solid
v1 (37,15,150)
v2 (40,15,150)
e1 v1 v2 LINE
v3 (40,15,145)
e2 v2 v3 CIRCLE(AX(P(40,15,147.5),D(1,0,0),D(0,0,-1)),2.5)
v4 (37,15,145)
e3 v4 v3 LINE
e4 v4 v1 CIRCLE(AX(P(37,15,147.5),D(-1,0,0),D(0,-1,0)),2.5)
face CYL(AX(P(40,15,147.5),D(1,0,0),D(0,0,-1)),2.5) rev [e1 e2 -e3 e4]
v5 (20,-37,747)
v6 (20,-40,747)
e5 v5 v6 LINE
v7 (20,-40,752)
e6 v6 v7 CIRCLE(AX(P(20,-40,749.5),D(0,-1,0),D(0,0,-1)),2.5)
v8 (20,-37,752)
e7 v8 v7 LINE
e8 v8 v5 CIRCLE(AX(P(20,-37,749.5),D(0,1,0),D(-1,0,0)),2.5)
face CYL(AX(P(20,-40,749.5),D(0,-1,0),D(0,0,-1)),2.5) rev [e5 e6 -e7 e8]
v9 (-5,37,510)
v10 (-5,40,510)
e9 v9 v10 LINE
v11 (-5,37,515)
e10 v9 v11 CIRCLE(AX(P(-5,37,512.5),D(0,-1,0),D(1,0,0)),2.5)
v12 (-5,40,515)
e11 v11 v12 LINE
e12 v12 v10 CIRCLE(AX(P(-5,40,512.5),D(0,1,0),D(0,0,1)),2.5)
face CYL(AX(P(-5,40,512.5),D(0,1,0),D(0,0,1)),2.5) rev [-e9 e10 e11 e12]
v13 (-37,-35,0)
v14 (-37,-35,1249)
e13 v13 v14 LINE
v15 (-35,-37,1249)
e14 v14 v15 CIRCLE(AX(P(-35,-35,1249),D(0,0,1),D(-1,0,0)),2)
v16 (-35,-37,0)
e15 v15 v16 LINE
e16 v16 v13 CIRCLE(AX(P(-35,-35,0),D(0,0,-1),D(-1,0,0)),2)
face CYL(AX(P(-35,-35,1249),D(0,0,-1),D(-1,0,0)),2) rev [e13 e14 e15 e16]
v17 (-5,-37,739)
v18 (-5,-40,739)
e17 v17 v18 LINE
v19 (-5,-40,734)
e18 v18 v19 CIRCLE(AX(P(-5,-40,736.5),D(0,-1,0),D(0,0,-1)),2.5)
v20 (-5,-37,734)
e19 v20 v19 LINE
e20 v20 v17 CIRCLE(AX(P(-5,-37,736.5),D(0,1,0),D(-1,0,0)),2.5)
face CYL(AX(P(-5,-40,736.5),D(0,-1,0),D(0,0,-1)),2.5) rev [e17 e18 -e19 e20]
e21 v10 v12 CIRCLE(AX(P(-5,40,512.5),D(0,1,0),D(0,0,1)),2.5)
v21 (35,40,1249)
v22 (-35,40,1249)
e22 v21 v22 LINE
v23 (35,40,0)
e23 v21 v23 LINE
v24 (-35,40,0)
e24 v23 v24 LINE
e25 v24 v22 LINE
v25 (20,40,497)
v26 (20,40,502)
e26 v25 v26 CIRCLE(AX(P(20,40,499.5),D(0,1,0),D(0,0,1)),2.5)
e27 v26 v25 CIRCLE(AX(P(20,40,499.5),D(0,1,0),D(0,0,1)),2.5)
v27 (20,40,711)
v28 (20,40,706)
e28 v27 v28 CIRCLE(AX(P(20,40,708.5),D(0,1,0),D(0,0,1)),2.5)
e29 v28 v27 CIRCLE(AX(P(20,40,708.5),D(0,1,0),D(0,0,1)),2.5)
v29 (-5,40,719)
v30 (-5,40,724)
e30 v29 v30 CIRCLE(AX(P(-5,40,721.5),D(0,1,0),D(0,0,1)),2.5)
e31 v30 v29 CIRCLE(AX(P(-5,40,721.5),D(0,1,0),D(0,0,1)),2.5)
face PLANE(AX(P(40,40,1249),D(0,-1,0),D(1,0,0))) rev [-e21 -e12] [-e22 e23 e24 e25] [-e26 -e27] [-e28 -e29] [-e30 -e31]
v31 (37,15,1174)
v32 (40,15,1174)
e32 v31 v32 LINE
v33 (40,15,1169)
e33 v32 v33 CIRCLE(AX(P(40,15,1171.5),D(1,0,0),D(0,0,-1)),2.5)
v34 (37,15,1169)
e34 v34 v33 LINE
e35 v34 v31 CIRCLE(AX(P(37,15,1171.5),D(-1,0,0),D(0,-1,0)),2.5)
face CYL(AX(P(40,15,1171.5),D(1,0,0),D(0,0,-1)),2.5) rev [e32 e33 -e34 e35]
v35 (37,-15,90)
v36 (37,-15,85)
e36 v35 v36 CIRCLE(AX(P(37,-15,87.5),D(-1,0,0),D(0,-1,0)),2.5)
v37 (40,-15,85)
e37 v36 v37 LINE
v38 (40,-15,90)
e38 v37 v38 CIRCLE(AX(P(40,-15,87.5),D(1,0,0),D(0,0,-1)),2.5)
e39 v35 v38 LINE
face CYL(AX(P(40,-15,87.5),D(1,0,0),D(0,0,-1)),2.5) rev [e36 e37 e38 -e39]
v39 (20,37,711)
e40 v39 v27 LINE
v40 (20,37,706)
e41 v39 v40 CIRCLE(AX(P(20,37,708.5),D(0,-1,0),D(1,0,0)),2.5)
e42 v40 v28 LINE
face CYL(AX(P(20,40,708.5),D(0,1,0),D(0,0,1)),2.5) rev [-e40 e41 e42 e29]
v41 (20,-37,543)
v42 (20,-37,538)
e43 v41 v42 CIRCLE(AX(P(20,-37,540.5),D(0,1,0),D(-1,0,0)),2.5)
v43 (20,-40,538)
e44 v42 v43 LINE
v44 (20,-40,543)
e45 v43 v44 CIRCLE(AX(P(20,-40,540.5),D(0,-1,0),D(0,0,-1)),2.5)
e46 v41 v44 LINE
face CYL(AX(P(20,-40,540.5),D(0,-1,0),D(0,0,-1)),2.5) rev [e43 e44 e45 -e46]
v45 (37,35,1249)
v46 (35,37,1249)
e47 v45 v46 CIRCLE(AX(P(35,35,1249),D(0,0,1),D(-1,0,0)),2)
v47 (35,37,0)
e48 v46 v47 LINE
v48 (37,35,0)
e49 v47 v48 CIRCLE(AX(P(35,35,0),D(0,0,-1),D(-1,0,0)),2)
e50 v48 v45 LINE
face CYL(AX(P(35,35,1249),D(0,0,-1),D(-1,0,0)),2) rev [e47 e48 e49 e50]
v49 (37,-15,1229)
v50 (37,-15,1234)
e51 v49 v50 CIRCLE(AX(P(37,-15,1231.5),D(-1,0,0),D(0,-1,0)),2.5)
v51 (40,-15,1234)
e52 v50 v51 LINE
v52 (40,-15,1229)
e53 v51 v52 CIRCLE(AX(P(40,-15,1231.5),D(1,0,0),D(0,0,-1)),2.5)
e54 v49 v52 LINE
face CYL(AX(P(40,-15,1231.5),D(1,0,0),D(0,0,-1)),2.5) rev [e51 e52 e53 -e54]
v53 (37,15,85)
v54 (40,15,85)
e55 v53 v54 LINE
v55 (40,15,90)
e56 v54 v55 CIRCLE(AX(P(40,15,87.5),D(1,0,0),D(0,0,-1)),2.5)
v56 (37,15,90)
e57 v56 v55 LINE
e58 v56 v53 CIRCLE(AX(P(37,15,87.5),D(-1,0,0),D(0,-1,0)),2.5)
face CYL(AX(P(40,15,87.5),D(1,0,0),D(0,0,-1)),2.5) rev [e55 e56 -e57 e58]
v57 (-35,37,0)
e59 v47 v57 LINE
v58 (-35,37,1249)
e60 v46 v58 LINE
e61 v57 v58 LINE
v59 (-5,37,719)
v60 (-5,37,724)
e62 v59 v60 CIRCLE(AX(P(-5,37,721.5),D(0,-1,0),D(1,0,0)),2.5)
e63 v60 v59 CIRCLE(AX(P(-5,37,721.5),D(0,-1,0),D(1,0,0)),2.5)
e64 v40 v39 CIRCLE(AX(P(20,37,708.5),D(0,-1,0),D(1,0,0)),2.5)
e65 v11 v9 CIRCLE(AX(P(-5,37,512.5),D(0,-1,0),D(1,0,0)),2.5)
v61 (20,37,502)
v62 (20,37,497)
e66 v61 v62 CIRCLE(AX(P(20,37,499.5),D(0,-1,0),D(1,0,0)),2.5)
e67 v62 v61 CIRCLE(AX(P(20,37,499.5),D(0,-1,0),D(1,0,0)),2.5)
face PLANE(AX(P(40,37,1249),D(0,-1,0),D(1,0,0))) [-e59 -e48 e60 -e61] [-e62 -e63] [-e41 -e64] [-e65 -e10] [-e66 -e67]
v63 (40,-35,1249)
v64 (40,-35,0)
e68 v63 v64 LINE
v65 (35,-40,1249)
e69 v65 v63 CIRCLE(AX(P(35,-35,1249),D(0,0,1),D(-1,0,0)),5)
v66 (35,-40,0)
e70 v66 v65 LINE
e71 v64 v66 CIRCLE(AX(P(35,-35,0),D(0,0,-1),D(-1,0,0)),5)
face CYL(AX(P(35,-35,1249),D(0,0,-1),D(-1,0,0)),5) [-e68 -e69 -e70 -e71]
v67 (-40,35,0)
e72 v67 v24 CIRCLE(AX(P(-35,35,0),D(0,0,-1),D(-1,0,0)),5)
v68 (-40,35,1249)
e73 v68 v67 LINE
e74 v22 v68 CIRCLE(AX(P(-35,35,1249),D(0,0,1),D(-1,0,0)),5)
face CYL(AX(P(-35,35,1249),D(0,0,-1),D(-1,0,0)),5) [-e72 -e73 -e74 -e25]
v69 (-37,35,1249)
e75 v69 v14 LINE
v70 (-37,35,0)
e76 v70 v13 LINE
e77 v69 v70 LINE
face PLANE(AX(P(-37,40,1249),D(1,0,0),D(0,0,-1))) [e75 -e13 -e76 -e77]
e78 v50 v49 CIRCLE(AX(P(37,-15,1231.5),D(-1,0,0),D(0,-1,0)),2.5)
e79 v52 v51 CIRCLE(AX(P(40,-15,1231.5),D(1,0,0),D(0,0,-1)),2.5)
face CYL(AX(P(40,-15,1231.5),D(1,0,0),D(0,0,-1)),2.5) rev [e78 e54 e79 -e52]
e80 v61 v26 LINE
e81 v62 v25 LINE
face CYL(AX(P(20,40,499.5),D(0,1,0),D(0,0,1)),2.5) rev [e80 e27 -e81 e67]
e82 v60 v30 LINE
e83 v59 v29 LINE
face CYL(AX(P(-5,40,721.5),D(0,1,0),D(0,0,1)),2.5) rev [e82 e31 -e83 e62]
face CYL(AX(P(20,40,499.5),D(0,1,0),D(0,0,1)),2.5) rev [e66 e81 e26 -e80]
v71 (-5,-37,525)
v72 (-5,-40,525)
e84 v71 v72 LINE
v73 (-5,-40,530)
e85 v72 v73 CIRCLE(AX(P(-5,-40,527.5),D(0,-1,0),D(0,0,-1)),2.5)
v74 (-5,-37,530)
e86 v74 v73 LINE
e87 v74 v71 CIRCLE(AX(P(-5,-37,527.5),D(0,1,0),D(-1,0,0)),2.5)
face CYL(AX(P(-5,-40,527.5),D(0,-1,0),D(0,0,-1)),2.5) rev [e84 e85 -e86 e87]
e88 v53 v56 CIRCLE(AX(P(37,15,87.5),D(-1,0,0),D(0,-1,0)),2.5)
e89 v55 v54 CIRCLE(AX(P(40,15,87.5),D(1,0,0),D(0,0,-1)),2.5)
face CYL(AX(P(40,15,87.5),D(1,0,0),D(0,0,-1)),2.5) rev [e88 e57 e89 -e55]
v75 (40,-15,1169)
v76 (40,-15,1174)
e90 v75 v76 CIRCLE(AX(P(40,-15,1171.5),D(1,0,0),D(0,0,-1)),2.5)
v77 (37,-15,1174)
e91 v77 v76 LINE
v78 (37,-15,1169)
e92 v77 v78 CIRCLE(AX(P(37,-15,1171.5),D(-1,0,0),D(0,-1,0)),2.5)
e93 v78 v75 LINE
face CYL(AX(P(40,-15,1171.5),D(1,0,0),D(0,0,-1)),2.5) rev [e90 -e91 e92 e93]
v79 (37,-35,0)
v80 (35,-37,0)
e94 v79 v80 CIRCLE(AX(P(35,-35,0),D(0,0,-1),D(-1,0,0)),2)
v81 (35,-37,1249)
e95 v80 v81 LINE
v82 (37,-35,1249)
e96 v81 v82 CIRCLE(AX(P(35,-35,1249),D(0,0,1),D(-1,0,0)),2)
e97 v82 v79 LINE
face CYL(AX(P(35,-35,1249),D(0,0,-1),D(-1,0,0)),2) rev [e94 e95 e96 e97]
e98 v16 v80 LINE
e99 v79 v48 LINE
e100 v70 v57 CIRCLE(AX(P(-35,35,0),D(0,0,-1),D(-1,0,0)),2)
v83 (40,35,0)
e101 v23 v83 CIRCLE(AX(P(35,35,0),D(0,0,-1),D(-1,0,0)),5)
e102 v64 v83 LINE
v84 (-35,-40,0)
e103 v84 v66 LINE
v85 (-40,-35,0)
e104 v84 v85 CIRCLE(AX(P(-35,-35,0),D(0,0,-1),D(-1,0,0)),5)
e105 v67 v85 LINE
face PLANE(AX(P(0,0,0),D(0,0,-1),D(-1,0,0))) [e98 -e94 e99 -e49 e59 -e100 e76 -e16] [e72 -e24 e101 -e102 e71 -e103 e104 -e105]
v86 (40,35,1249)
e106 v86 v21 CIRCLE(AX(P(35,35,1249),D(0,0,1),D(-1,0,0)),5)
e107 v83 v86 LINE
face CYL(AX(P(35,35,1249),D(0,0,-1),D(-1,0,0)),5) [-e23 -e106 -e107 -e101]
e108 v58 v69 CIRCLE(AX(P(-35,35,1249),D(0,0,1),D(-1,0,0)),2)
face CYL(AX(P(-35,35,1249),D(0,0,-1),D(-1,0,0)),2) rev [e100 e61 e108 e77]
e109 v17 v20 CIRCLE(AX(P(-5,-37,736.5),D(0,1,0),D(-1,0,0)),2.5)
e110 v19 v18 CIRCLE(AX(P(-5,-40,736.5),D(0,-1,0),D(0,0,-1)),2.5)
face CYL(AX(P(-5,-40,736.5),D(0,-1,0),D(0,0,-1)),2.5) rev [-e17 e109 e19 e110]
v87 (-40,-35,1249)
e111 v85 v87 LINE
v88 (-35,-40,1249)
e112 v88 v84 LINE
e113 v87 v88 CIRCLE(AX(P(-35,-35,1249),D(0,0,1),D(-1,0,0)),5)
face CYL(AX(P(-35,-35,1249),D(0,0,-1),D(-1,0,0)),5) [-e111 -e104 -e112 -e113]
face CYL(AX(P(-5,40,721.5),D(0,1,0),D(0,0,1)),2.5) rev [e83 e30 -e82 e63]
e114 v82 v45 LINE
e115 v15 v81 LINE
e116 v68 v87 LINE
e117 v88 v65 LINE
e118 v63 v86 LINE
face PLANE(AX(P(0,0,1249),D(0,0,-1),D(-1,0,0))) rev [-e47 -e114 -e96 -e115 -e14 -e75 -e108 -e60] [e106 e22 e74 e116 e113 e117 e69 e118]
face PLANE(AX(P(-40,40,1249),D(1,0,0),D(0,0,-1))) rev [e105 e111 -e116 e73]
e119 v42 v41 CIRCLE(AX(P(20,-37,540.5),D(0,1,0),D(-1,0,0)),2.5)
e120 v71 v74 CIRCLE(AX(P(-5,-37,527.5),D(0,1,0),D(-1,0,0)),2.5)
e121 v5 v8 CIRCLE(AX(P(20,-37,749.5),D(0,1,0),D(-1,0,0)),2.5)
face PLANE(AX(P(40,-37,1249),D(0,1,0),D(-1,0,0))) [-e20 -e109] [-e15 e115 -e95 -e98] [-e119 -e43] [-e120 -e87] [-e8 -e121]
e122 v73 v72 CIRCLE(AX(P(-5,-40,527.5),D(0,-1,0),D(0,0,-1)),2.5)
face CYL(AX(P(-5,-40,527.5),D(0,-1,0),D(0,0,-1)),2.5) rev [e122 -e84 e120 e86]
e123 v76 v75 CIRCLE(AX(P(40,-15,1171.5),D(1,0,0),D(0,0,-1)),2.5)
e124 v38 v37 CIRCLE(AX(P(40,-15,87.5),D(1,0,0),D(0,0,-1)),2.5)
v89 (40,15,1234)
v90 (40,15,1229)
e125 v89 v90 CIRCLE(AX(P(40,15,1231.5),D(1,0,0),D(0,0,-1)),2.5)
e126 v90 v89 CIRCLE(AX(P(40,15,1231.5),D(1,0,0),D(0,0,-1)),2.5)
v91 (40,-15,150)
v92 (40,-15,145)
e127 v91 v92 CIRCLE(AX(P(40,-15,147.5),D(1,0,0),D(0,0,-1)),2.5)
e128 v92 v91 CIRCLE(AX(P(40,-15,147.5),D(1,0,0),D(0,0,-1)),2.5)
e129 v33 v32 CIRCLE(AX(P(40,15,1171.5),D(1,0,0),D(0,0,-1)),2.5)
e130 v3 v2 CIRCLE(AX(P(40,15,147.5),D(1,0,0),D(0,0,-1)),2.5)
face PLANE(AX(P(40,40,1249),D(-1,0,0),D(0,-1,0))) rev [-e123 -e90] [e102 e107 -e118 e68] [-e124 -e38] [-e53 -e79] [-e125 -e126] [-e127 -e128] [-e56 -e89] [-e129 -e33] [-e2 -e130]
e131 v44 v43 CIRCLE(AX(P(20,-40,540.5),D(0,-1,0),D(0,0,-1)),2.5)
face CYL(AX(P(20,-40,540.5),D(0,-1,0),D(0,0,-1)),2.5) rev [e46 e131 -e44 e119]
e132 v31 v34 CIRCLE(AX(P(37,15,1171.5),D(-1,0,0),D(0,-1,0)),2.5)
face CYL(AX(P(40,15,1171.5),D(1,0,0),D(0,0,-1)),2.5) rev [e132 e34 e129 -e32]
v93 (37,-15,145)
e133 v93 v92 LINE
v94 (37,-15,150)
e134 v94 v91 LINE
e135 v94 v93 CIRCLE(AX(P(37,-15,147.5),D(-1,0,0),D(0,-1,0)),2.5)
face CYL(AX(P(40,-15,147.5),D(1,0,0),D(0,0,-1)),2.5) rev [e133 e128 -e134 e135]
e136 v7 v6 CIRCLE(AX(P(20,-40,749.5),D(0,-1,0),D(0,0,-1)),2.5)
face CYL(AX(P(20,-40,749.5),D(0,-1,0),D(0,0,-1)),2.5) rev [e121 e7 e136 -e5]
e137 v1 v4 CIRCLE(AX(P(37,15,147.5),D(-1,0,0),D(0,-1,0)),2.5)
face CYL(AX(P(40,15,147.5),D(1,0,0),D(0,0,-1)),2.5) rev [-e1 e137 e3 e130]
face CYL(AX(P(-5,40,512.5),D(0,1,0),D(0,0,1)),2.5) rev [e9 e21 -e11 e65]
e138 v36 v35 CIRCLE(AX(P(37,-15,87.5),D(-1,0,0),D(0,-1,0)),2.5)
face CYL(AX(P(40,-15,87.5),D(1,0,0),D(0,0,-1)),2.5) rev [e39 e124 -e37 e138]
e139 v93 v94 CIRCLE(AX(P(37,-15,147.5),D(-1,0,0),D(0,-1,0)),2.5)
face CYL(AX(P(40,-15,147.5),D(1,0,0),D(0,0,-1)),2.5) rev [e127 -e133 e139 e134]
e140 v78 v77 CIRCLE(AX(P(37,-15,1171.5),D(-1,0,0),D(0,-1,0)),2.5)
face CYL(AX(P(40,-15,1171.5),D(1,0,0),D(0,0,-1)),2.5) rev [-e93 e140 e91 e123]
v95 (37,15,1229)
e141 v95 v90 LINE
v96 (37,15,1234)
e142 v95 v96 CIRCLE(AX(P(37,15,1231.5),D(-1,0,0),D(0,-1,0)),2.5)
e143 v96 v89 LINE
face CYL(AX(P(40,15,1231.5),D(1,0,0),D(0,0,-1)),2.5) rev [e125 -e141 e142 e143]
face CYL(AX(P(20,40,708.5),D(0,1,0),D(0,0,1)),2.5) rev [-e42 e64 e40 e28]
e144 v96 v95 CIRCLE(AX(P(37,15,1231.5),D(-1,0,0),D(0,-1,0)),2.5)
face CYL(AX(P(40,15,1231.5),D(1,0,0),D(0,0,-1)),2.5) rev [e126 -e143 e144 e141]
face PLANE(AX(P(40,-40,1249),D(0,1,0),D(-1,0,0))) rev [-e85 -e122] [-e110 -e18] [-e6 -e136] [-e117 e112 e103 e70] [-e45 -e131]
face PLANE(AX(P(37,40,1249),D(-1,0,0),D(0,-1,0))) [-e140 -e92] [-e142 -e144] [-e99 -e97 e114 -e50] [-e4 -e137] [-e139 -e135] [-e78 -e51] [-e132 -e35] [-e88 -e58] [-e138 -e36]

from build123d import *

# Parameters (mm, degrees)
SKETCH_1_W             = 80
SKETCH_1_H             = 80
EXTRUDE_1_DEPTH        = 1249
FILLET_1_R             = 5
SHELL_1_T              = -3
HOLE_WIZARD_M6_1_D     = 5
HOLE_WIZARD_M6_1_DEPTH = 15
HOLE_WIZARD_M6_1_TIP   = 1.502151548
HOLE_WIZARD_M6_2_D     = 5
HOLE_WIZARD_M6_2_DEPTH = 15
HOLE_WIZARD_M6_2_TIP   = 1.502151548
HOLE_WIZARD_M6_3_D     = 5
HOLE_WIZARD_M6_3_DEPTH = 15
HOLE_WIZARD_M6_3_TIP   = 1.502151548


with BuildPart() as part:
    # 草图1 → 凸台-拉伸1 (new body)
    with BuildSketch(Plane.XY):
        Rectangle(SKETCH_1_W, SKETCH_1_H)
    extrude(amount=EXTRUDE_1_DEPTH)

    # 圆角1
    fillet_1_edges = [part.edges().sort_by_distance(p)[0] for p in [
        (-40, 40, 624.5),
        (40, 40, 624.5),
        (40, -40, 624.5),
        (-40, -40, 624.5),
    ]]
    fillet(fillet_1_edges, radius=FILLET_1_R)

    # 抽壳1
    shell_1_openings = [part.faces().sort_by_distance(p)[0] for p in [
        (0, 0, 1249),
        (0, 0, 0),
    ]]
    offset(amount=SHELL_1_T, openings=shell_1_openings, kind=Kind.INTERSECTION)

    # M6 螺纹孔1
    with Locations(Plane(origin=(40, 0, 0), x_dir=(0, 0, -1), z_dir=(1, 0, 0))):
        with Locations((-147.5, 15), (-87.5, 15), (-87.5, -15), (-147.5, -15), (-1171.5, 15), (-1171.5, -15), (-1231.5, -15), (-1231.5, 15)):
            Hole(HOLE_WIZARD_M6_1_D / 2, depth=HOLE_WIZARD_M6_1_DEPTH)
            with Locations((0, 0, -(HOLE_WIZARD_M6_1_DEPTH + HOLE_WIZARD_M6_1_TIP / 2))):  # 118° drill point
                Cone(0, HOLE_WIZARD_M6_1_D / 2, HOLE_WIZARD_M6_1_TIP, mode=Mode.SUBTRACT)

    # M6 螺纹孔2
    with Locations(Plane(origin=(0, -40, 0), x_dir=(-1, 0, 0), z_dir=(0, -1, 0))):
        with Locations((-20, -749.5), (5, -736.5), (-20, -540.5), (5, -527.5)):
            Hole(HOLE_WIZARD_M6_2_D / 2, depth=HOLE_WIZARD_M6_2_DEPTH)
            with Locations((0, 0, -(HOLE_WIZARD_M6_2_DEPTH + HOLE_WIZARD_M6_2_TIP / 2))):  # 118° drill point
                Cone(0, HOLE_WIZARD_M6_2_D / 2, HOLE_WIZARD_M6_2_TIP, mode=Mode.SUBTRACT)

    # M6 螺纹孔3
    with Locations(Plane(origin=(0, 40, 0), x_dir=(1, 0, 0), z_dir=(0, 1, 0))):
        with Locations((-5, -721.5), (20, -708.5), (20, -499.5), (-5, -512.5)):
            Hole(HOLE_WIZARD_M6_3_D / 2, depth=HOLE_WIZARD_M6_3_DEPTH)
            with Locations((0, 0, -(HOLE_WIZARD_M6_3_DEPTH + HOLE_WIZARD_M6_3_TIP / 2))):  # 118° drill point
                Cone(0, HOLE_WIZARD_M6_3_D / 2, HOLE_WIZARD_M6_3_TIP, mode=Mode.SUBTRACT)


solid = part.part
